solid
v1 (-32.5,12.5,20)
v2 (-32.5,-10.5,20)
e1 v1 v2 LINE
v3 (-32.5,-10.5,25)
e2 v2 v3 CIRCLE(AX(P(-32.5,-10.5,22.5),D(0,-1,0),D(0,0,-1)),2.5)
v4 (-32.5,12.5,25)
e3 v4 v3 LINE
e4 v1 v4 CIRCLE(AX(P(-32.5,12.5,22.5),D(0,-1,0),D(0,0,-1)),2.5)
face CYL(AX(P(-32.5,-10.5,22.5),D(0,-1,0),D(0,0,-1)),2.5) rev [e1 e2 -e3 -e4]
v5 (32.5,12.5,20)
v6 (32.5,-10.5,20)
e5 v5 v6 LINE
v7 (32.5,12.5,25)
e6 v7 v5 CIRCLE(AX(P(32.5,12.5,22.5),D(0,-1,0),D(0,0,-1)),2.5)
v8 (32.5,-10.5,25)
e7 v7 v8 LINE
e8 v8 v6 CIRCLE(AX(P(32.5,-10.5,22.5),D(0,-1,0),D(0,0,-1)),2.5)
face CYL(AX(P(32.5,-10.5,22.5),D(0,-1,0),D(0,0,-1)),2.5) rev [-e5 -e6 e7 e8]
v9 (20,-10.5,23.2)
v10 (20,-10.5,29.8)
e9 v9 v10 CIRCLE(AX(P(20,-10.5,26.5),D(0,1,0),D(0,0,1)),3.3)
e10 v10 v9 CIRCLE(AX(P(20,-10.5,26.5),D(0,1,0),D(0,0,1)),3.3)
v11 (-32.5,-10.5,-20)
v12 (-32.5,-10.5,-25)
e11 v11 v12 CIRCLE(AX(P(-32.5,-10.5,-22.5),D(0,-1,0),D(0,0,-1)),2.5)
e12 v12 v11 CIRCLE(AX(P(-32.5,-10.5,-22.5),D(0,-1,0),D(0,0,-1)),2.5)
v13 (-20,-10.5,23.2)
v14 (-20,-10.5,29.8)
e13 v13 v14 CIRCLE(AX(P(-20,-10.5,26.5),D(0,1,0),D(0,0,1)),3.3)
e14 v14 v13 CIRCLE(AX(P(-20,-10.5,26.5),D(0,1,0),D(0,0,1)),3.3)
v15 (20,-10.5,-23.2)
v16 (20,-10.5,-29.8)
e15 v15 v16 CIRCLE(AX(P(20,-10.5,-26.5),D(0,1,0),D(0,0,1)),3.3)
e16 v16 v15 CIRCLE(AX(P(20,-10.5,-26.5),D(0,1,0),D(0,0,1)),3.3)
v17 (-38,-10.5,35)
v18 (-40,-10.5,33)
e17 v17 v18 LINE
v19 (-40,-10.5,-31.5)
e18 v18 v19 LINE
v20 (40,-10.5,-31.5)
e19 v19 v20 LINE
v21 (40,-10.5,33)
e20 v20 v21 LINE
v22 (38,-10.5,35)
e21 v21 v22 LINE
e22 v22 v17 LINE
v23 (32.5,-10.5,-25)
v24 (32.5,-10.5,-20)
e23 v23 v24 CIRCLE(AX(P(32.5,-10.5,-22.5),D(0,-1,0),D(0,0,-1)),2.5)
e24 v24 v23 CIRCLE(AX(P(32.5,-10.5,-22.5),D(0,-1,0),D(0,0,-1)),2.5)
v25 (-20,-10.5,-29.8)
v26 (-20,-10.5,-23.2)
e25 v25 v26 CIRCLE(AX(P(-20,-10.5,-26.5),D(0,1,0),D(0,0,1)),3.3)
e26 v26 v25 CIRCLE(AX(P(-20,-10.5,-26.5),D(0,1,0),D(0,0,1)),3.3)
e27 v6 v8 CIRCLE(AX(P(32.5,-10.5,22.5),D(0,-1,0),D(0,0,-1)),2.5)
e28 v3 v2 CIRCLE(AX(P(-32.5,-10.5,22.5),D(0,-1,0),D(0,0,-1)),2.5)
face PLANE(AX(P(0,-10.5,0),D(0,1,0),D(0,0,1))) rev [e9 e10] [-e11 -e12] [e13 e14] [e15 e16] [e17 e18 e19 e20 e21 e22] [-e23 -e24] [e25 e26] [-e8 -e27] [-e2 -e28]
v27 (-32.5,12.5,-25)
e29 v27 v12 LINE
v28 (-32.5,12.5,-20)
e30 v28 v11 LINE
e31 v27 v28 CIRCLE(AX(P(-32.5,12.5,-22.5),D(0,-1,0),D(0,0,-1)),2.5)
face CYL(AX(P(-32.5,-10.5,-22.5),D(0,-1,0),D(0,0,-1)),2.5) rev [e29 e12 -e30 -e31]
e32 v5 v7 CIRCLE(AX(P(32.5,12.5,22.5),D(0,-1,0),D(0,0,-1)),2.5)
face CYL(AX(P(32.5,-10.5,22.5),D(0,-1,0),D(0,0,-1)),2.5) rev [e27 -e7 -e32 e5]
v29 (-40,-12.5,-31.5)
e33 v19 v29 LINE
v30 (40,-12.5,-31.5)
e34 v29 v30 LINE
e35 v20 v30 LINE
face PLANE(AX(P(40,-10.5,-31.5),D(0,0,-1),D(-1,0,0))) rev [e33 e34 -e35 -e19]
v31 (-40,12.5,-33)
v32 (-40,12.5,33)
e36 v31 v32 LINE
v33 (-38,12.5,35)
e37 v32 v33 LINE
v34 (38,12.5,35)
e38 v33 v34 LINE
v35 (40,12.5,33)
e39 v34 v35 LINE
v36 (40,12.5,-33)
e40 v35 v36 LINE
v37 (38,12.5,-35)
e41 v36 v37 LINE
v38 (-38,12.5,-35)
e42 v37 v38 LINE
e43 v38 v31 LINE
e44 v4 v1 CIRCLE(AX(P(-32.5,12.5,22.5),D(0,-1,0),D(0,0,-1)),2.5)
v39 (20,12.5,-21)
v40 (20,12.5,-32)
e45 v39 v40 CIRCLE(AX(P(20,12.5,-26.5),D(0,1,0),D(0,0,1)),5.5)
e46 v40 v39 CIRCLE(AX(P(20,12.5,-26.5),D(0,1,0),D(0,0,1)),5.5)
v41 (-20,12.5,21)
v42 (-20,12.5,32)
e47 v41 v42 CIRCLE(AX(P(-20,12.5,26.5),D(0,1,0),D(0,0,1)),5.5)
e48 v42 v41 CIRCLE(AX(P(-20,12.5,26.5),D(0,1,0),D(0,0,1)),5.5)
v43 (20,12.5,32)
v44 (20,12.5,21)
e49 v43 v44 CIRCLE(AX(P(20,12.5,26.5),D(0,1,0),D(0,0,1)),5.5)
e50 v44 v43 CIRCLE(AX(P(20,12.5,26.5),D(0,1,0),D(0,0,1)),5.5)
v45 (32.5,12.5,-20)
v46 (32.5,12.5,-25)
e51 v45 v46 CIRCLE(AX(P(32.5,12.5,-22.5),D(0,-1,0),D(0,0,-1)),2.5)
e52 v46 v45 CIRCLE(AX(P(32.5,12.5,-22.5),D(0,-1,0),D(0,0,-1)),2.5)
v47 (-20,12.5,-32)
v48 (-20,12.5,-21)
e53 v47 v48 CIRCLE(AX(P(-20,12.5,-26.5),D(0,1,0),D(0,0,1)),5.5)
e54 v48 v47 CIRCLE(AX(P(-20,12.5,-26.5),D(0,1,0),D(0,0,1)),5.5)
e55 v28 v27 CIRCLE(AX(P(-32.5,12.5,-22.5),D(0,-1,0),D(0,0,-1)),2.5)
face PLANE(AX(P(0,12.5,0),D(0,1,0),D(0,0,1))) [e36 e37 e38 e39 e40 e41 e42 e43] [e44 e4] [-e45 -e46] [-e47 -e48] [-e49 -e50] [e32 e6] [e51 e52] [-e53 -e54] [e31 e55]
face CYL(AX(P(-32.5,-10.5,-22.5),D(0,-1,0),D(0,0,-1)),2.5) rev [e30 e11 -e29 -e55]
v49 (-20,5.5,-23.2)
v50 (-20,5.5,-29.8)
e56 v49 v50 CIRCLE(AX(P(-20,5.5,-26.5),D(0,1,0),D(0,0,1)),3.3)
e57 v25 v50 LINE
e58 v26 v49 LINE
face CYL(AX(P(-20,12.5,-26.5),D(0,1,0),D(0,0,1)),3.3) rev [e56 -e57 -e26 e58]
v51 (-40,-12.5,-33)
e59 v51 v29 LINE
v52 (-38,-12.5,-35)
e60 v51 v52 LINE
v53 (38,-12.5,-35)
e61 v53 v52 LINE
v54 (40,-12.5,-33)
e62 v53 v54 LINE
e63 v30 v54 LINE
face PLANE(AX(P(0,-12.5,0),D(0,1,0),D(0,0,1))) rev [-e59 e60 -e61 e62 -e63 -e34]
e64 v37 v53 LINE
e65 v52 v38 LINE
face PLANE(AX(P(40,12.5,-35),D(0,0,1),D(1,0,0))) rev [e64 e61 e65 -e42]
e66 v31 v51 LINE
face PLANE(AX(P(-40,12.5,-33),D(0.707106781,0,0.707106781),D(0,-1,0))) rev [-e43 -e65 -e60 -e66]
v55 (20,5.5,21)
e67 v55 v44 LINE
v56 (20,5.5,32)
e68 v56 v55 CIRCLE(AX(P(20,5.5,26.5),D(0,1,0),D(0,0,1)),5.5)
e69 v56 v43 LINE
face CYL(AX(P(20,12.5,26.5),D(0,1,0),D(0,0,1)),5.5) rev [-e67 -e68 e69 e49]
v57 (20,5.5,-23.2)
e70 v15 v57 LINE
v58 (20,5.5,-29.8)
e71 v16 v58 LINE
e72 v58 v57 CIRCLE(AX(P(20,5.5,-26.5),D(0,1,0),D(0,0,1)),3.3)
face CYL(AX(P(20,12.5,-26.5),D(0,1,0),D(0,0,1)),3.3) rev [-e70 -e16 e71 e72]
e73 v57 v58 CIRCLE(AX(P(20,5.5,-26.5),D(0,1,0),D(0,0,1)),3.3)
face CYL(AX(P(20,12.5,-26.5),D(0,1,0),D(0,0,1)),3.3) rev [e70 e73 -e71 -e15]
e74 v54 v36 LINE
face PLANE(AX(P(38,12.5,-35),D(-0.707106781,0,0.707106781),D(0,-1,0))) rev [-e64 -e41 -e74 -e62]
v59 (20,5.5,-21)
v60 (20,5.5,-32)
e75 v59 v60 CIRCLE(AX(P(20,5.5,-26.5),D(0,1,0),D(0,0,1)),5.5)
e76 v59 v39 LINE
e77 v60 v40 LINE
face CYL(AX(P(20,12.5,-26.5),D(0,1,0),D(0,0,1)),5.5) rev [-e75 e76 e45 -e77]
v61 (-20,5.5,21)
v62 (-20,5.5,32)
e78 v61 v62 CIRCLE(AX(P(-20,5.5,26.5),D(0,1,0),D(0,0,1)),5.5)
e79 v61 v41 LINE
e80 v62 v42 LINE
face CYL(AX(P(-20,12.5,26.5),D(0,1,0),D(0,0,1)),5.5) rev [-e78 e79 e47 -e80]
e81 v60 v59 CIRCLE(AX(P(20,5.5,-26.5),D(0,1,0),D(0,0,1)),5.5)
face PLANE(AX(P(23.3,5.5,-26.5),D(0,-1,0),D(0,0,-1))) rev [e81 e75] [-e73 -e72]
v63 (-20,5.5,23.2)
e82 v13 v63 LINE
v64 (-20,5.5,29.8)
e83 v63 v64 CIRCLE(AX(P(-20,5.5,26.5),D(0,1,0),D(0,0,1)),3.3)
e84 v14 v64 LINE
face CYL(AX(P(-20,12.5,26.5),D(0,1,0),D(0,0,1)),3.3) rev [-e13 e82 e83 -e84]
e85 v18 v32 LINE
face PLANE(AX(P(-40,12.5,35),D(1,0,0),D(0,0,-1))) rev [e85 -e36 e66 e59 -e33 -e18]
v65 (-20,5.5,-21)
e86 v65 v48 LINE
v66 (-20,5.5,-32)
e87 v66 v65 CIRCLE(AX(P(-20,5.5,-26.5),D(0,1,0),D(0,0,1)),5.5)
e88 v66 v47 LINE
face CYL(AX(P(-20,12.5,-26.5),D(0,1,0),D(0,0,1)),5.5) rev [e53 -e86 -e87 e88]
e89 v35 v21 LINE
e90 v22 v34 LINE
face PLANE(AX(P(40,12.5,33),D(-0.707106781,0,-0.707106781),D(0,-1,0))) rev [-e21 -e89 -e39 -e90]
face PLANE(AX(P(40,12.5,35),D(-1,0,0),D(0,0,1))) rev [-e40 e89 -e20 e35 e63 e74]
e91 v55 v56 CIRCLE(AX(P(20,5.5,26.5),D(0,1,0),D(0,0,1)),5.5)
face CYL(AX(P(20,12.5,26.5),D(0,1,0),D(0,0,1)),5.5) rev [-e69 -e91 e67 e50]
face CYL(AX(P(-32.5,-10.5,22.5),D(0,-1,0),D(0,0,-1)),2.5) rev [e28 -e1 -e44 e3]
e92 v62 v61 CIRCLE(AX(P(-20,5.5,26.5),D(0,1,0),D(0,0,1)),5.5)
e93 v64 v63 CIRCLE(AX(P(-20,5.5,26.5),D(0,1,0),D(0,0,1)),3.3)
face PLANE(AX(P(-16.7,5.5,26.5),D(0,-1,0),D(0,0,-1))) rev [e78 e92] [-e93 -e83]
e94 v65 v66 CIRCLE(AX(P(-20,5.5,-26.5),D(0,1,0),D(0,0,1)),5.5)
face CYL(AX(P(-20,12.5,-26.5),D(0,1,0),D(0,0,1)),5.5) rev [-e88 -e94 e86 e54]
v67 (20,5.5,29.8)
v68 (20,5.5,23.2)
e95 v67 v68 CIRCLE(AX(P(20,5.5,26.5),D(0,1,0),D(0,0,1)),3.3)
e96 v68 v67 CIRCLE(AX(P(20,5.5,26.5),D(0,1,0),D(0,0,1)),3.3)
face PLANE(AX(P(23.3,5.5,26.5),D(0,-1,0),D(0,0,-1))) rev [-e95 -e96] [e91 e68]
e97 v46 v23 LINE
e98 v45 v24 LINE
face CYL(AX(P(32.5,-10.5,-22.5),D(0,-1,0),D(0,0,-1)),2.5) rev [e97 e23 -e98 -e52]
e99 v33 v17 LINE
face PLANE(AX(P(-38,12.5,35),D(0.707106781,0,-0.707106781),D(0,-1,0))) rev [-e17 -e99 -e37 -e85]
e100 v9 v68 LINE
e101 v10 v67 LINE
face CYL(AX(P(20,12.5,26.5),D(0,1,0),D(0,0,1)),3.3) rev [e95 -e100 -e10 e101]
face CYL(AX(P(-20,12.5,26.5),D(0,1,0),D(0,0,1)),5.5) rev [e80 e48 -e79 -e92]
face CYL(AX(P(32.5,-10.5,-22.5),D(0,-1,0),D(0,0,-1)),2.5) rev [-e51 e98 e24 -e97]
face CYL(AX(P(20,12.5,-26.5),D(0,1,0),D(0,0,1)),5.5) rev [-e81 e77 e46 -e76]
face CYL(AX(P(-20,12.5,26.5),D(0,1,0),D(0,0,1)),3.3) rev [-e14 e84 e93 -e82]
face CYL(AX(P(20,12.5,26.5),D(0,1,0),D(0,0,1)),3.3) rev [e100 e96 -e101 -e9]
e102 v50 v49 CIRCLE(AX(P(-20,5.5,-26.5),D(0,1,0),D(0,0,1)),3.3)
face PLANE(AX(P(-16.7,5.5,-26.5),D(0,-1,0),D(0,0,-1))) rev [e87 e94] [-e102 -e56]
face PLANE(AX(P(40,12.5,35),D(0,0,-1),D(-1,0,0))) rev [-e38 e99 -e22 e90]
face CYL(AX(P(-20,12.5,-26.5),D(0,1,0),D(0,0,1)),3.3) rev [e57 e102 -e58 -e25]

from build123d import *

# Parameters (mm, degrees)
SKETCH_1_W                = 80
SKETCH_1_H                = 70
EXTRUDE_1_DEPTH           = 12.5
SKETCH_3_W                = 80
SKETCH_3_H                = 66.5
CUT_EXTRUDE_1_DEPTH       = 2
HOLE_WIZARD_M5_1_D        = 4.2
HOLE_WIZARD_M6_1_D        = 5
CHAMFER_1_SIZE            = 2
HOLE_WIZARD_1_D           = 6.6
HOLE_WIZARD_1_DEPTH       = 25
HOLE_WIZARD_1_CBORE_D     = 11
HOLE_WIZARD_1_CBORE_DEPTH = 7


with BuildPart() as part:
    # 草图1 → 凸台-拉伸1 (new, symmetric)
    with BuildSketch(Plane(origin=(0, 0, 0), x_dir=(1, 0, 0), z_dir=(0, 1, 0))):
        Rectangle(SKETCH_1_W, SKETCH_1_H)
    extrude(amount=EXTRUDE_1_DEPTH, both=True)

    # 草图3 → 切除-拉伸1 (cut)
    with BuildSketch(Plane.XZ.offset(12.5)):
        with Locations((0, 1.75)):
            Rectangle(SKETCH_3_W, SKETCH_3_H)
    extrude(amount=-CUT_EXTRUDE_1_DEPTH, mode=Mode.SUBTRACT)

    # M5 螺纹孔1 (through all)
    with Locations(Plane(origin=(0, -10.5, 0), x_dir=(-1, 0, 0), z_dir=(0, -1, 0))):
        with Locations((20, 26.5), (-20, 26.5), (-20, -26.5), (20, -26.5)):
            Hole(HOLE_WIZARD_M5_1_D / 2)

    # M6 螺纹孔1 (through all)
    with Locations(Plane(origin=(0, -10.5, 0), x_dir=(-1, 0, 0), z_dir=(0, -1, 0))):
        with Locations((32.5, 22.5), (32.5, -22.5), (-32.5, 22.5), (-32.5, -22.5)):
            Hole(HOLE_WIZARD_M6_1_D / 2)

    # 倒角1
    chamfer_1_edges = [part.edges().sort_by_distance(p)[0] for p in [
        (-40, 0, -35),
        (40, 0, -35),
        (40, 1, 35),
        (-40, 1, 35),
    ]]
    chamfer(chamfer_1_edges, length=CHAMFER_1_SIZE)

    # 打孔尺寸(%根据)内六角花形圆柱头螺钉1
    with Locations(Plane(origin=(0, 12.5, 0), x_dir=(1, 0, 0), z_dir=(0, 1, 0))):
        with Locations((20, 26.5), (20, -26.5), (-20, -26.5), (-20, 26.5)):
            CounterBoreHole(HOLE_WIZARD_1_D / 2, HOLE_WIZARD_1_CBORE_D / 2, HOLE_WIZARD_1_CBORE_DEPTH, depth=HOLE_WIZARD_1_DEPTH)


solid = part.part
